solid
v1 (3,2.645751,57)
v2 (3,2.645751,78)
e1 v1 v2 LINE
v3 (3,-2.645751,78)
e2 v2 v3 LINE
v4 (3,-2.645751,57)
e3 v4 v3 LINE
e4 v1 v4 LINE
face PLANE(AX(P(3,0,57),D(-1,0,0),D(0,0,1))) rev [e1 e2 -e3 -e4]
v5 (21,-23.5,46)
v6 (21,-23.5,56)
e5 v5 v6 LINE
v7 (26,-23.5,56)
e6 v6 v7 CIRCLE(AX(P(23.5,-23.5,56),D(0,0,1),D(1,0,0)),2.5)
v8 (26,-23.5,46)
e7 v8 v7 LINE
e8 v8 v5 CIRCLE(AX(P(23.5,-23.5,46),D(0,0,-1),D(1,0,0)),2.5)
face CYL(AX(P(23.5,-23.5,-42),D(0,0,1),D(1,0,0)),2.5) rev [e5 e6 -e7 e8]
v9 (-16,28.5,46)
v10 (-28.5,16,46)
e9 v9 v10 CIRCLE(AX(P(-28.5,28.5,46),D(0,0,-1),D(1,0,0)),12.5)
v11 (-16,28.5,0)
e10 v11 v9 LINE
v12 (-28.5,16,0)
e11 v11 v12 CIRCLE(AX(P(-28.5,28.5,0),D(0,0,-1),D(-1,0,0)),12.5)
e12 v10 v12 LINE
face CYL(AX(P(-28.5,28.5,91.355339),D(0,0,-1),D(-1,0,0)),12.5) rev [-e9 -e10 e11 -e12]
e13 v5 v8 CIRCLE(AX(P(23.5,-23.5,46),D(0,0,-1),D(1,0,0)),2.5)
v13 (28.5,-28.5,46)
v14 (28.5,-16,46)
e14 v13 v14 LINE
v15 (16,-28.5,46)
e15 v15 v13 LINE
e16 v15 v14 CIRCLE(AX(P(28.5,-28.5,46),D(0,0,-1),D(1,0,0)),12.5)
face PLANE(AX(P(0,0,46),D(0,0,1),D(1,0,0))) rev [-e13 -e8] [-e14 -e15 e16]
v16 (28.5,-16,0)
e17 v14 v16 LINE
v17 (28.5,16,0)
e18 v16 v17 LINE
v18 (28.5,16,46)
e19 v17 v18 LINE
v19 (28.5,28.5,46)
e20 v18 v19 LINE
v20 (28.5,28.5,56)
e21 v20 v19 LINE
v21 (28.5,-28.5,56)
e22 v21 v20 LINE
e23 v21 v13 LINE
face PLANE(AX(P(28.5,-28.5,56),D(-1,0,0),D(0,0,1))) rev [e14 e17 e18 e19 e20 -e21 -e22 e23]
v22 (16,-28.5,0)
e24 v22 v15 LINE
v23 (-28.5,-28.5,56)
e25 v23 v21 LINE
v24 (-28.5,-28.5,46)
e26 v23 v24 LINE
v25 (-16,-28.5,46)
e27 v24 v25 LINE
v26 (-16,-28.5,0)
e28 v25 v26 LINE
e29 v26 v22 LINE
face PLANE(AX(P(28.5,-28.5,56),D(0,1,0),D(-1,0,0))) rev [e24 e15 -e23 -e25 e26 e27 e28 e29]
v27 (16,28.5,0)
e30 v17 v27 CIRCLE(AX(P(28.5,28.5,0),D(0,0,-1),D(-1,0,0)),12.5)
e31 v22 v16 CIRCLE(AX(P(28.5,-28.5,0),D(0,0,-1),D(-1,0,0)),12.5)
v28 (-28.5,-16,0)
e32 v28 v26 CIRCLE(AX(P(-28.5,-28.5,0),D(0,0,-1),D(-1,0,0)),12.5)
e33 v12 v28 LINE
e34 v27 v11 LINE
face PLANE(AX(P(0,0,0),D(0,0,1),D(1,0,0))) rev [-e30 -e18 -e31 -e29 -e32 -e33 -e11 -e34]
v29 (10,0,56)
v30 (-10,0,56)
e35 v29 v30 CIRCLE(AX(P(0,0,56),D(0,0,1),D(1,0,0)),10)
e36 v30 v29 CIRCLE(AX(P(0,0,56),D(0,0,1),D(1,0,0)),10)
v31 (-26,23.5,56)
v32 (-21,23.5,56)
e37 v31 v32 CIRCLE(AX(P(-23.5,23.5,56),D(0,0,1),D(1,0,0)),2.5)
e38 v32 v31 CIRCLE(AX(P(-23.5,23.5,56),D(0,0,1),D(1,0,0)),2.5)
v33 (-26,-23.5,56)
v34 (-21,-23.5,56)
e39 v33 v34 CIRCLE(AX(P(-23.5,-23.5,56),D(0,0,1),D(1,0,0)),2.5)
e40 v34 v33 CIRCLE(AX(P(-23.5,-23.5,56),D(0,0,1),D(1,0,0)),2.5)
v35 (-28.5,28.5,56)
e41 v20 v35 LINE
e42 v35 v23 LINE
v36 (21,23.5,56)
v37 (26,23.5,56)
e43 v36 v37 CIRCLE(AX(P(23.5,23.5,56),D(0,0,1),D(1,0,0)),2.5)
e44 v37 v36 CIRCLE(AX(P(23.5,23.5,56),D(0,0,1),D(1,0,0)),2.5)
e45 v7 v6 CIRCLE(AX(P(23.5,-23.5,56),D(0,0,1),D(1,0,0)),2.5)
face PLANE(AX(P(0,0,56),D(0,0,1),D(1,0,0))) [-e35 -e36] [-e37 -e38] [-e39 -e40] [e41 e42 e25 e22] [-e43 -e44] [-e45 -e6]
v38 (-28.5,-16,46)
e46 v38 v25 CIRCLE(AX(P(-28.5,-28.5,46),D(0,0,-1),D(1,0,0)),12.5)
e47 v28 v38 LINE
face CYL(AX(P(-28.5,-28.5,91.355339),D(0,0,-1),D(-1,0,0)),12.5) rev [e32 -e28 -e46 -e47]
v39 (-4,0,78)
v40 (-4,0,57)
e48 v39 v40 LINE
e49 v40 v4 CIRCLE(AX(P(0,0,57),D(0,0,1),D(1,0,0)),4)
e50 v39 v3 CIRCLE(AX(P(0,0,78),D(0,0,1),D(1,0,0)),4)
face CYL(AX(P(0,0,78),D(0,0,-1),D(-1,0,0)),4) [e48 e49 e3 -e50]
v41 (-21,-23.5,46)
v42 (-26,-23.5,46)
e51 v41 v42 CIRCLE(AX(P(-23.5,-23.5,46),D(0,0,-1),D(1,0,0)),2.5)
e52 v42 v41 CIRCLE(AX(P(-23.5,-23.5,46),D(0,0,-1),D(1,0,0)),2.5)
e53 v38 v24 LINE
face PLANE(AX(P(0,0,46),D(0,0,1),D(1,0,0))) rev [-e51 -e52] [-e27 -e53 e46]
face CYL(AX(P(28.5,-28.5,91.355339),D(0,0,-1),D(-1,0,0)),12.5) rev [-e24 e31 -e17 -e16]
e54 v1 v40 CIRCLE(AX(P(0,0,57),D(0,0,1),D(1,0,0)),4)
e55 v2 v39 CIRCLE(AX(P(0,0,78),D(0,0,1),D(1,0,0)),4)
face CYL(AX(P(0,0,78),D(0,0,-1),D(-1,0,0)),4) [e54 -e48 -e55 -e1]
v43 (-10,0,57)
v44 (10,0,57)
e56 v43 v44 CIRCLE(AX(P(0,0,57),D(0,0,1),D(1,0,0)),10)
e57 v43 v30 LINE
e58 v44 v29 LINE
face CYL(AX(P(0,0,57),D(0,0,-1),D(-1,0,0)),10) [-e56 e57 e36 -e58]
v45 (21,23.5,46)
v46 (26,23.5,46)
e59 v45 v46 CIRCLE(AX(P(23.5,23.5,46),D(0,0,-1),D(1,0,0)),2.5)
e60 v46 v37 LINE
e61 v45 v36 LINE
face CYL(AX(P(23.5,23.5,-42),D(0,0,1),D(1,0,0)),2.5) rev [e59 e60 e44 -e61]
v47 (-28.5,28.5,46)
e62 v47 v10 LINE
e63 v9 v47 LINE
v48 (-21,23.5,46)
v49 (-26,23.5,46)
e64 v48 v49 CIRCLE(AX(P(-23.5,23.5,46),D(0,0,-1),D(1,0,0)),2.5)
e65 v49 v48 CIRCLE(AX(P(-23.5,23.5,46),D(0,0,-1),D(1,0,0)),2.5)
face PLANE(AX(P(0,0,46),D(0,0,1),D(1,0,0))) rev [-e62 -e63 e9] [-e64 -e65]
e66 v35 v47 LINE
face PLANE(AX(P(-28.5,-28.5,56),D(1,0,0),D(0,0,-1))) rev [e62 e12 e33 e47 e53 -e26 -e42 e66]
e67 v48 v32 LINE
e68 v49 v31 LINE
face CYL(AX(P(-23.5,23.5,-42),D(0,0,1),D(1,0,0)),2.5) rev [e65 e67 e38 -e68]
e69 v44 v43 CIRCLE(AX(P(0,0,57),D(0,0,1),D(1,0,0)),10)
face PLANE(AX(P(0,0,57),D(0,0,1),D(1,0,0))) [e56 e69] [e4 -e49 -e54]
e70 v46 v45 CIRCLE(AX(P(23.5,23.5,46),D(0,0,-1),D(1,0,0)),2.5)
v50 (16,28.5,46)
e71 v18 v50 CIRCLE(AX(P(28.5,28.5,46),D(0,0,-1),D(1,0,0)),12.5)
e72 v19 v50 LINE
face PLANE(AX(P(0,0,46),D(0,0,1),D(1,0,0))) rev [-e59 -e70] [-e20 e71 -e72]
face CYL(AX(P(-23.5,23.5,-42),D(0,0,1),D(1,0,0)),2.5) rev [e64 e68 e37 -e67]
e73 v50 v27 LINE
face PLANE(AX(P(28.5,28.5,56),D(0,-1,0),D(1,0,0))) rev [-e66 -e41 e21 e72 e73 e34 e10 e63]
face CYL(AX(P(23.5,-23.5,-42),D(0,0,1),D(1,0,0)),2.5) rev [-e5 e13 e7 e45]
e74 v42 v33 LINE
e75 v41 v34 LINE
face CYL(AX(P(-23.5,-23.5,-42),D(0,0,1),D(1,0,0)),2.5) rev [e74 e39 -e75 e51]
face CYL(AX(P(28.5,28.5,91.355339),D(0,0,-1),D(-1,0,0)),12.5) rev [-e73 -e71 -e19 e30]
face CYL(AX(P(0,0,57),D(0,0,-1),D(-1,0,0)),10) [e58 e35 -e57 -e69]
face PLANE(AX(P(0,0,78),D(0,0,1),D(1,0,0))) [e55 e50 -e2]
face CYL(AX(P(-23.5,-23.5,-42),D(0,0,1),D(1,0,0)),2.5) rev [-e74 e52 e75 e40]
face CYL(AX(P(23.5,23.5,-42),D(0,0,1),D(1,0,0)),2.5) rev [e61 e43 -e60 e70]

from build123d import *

# Parameters (mm, degrees)
SKETCH1_W           = 57
SKETCH1_H           = 57
BOSS_EXTRUDE1_DEPTH = 56
SKETCH2_R           = 2.5
CUT_EXTRUDE1_DEPTH  = 98
SKETCH4_R           = 10
BOSS_EXTRUDE2_DEPTH = 1
SKETCH5_R           = 4
BOSS_EXTRUDE3_DEPTH = 21
CUT_EXTRUDE2_DEPTH  = 21
SKETCH7_R           = 12.5
CUT_EXTRUDE3_DEPTH  = 46


with BuildPart() as part:
    # Sketch1 → Boss-Extrude1 (new body)
    with BuildSketch(Plane.XY):
        Rectangle(SKETCH1_W, SKETCH1_H)
    extrude(amount=BOSS_EXTRUDE1_DEPTH)

    # Sketch2 → Cut-Extrude1 (cut)
    with BuildSketch(Plane.XY.offset(56)):
        with Locations((-23.5, 23.5)):
            Circle(SKETCH2_R)
        with Locations((23.5, 23.5)):
            Circle(SKETCH2_R)
        with Locations((23.5, -23.5)):
            Circle(SKETCH2_R)
        with Locations((-23.5, -23.5)):
            Circle(SKETCH2_R)
    extrude(amount=-CUT_EXTRUDE1_DEPTH, mode=Mode.SUBTRACT)

    # Sketch4 → Boss-Extrude2 (add)
    with BuildSketch(Plane.XY.offset(56)):
        Circle(SKETCH4_R)
    extrude(amount=BOSS_EXTRUDE2_DEPTH)

    # Sketch5 → Boss-Extrude3 (add)
    with BuildSketch(Plane.XY.offset(57)):
        with Locations(Location((0, 0, 0), (0, 0, 180))):
            Circle(SKETCH5_R)
    extrude(amount=BOSS_EXTRUDE3_DEPTH)

    # Sketch6 → Cut-Extrude2 (cut)
    with BuildSketch(Plane.XY.offset(78)):
        Polygon((3, 101.241638907), (3, 2.645751311), (3, -2.645751311), (3, -101.241638907), (200.191775192, -101.241638907), (200.191775192, 101.241638907), align=None)
    extrude(amount=-CUT_EXTRUDE2_DEPTH, mode=Mode.SUBTRACT)

    # Sketch7 → Cut-Extrude3 (cut)
    with BuildSketch(Plane(origin=(0, 0, 0), x_dir=(-1, 0, 0), z_dir=(0, 0, -1))):
        with Locations((-28.5, 28.5)):
            Circle(SKETCH7_R)
        with Locations((28.5, 28.5)):
            Circle(SKETCH7_R)
        with Locations((28.5, -28.5)):
            Circle(SKETCH7_R)
        with Locations((-28.5, -28.5)):
            Circle(SKETCH7_R)
    extrude(amount=-CUT_EXTRUDE3_DEPTH, mode=Mode.SUBTRACT)


solid = part.part
